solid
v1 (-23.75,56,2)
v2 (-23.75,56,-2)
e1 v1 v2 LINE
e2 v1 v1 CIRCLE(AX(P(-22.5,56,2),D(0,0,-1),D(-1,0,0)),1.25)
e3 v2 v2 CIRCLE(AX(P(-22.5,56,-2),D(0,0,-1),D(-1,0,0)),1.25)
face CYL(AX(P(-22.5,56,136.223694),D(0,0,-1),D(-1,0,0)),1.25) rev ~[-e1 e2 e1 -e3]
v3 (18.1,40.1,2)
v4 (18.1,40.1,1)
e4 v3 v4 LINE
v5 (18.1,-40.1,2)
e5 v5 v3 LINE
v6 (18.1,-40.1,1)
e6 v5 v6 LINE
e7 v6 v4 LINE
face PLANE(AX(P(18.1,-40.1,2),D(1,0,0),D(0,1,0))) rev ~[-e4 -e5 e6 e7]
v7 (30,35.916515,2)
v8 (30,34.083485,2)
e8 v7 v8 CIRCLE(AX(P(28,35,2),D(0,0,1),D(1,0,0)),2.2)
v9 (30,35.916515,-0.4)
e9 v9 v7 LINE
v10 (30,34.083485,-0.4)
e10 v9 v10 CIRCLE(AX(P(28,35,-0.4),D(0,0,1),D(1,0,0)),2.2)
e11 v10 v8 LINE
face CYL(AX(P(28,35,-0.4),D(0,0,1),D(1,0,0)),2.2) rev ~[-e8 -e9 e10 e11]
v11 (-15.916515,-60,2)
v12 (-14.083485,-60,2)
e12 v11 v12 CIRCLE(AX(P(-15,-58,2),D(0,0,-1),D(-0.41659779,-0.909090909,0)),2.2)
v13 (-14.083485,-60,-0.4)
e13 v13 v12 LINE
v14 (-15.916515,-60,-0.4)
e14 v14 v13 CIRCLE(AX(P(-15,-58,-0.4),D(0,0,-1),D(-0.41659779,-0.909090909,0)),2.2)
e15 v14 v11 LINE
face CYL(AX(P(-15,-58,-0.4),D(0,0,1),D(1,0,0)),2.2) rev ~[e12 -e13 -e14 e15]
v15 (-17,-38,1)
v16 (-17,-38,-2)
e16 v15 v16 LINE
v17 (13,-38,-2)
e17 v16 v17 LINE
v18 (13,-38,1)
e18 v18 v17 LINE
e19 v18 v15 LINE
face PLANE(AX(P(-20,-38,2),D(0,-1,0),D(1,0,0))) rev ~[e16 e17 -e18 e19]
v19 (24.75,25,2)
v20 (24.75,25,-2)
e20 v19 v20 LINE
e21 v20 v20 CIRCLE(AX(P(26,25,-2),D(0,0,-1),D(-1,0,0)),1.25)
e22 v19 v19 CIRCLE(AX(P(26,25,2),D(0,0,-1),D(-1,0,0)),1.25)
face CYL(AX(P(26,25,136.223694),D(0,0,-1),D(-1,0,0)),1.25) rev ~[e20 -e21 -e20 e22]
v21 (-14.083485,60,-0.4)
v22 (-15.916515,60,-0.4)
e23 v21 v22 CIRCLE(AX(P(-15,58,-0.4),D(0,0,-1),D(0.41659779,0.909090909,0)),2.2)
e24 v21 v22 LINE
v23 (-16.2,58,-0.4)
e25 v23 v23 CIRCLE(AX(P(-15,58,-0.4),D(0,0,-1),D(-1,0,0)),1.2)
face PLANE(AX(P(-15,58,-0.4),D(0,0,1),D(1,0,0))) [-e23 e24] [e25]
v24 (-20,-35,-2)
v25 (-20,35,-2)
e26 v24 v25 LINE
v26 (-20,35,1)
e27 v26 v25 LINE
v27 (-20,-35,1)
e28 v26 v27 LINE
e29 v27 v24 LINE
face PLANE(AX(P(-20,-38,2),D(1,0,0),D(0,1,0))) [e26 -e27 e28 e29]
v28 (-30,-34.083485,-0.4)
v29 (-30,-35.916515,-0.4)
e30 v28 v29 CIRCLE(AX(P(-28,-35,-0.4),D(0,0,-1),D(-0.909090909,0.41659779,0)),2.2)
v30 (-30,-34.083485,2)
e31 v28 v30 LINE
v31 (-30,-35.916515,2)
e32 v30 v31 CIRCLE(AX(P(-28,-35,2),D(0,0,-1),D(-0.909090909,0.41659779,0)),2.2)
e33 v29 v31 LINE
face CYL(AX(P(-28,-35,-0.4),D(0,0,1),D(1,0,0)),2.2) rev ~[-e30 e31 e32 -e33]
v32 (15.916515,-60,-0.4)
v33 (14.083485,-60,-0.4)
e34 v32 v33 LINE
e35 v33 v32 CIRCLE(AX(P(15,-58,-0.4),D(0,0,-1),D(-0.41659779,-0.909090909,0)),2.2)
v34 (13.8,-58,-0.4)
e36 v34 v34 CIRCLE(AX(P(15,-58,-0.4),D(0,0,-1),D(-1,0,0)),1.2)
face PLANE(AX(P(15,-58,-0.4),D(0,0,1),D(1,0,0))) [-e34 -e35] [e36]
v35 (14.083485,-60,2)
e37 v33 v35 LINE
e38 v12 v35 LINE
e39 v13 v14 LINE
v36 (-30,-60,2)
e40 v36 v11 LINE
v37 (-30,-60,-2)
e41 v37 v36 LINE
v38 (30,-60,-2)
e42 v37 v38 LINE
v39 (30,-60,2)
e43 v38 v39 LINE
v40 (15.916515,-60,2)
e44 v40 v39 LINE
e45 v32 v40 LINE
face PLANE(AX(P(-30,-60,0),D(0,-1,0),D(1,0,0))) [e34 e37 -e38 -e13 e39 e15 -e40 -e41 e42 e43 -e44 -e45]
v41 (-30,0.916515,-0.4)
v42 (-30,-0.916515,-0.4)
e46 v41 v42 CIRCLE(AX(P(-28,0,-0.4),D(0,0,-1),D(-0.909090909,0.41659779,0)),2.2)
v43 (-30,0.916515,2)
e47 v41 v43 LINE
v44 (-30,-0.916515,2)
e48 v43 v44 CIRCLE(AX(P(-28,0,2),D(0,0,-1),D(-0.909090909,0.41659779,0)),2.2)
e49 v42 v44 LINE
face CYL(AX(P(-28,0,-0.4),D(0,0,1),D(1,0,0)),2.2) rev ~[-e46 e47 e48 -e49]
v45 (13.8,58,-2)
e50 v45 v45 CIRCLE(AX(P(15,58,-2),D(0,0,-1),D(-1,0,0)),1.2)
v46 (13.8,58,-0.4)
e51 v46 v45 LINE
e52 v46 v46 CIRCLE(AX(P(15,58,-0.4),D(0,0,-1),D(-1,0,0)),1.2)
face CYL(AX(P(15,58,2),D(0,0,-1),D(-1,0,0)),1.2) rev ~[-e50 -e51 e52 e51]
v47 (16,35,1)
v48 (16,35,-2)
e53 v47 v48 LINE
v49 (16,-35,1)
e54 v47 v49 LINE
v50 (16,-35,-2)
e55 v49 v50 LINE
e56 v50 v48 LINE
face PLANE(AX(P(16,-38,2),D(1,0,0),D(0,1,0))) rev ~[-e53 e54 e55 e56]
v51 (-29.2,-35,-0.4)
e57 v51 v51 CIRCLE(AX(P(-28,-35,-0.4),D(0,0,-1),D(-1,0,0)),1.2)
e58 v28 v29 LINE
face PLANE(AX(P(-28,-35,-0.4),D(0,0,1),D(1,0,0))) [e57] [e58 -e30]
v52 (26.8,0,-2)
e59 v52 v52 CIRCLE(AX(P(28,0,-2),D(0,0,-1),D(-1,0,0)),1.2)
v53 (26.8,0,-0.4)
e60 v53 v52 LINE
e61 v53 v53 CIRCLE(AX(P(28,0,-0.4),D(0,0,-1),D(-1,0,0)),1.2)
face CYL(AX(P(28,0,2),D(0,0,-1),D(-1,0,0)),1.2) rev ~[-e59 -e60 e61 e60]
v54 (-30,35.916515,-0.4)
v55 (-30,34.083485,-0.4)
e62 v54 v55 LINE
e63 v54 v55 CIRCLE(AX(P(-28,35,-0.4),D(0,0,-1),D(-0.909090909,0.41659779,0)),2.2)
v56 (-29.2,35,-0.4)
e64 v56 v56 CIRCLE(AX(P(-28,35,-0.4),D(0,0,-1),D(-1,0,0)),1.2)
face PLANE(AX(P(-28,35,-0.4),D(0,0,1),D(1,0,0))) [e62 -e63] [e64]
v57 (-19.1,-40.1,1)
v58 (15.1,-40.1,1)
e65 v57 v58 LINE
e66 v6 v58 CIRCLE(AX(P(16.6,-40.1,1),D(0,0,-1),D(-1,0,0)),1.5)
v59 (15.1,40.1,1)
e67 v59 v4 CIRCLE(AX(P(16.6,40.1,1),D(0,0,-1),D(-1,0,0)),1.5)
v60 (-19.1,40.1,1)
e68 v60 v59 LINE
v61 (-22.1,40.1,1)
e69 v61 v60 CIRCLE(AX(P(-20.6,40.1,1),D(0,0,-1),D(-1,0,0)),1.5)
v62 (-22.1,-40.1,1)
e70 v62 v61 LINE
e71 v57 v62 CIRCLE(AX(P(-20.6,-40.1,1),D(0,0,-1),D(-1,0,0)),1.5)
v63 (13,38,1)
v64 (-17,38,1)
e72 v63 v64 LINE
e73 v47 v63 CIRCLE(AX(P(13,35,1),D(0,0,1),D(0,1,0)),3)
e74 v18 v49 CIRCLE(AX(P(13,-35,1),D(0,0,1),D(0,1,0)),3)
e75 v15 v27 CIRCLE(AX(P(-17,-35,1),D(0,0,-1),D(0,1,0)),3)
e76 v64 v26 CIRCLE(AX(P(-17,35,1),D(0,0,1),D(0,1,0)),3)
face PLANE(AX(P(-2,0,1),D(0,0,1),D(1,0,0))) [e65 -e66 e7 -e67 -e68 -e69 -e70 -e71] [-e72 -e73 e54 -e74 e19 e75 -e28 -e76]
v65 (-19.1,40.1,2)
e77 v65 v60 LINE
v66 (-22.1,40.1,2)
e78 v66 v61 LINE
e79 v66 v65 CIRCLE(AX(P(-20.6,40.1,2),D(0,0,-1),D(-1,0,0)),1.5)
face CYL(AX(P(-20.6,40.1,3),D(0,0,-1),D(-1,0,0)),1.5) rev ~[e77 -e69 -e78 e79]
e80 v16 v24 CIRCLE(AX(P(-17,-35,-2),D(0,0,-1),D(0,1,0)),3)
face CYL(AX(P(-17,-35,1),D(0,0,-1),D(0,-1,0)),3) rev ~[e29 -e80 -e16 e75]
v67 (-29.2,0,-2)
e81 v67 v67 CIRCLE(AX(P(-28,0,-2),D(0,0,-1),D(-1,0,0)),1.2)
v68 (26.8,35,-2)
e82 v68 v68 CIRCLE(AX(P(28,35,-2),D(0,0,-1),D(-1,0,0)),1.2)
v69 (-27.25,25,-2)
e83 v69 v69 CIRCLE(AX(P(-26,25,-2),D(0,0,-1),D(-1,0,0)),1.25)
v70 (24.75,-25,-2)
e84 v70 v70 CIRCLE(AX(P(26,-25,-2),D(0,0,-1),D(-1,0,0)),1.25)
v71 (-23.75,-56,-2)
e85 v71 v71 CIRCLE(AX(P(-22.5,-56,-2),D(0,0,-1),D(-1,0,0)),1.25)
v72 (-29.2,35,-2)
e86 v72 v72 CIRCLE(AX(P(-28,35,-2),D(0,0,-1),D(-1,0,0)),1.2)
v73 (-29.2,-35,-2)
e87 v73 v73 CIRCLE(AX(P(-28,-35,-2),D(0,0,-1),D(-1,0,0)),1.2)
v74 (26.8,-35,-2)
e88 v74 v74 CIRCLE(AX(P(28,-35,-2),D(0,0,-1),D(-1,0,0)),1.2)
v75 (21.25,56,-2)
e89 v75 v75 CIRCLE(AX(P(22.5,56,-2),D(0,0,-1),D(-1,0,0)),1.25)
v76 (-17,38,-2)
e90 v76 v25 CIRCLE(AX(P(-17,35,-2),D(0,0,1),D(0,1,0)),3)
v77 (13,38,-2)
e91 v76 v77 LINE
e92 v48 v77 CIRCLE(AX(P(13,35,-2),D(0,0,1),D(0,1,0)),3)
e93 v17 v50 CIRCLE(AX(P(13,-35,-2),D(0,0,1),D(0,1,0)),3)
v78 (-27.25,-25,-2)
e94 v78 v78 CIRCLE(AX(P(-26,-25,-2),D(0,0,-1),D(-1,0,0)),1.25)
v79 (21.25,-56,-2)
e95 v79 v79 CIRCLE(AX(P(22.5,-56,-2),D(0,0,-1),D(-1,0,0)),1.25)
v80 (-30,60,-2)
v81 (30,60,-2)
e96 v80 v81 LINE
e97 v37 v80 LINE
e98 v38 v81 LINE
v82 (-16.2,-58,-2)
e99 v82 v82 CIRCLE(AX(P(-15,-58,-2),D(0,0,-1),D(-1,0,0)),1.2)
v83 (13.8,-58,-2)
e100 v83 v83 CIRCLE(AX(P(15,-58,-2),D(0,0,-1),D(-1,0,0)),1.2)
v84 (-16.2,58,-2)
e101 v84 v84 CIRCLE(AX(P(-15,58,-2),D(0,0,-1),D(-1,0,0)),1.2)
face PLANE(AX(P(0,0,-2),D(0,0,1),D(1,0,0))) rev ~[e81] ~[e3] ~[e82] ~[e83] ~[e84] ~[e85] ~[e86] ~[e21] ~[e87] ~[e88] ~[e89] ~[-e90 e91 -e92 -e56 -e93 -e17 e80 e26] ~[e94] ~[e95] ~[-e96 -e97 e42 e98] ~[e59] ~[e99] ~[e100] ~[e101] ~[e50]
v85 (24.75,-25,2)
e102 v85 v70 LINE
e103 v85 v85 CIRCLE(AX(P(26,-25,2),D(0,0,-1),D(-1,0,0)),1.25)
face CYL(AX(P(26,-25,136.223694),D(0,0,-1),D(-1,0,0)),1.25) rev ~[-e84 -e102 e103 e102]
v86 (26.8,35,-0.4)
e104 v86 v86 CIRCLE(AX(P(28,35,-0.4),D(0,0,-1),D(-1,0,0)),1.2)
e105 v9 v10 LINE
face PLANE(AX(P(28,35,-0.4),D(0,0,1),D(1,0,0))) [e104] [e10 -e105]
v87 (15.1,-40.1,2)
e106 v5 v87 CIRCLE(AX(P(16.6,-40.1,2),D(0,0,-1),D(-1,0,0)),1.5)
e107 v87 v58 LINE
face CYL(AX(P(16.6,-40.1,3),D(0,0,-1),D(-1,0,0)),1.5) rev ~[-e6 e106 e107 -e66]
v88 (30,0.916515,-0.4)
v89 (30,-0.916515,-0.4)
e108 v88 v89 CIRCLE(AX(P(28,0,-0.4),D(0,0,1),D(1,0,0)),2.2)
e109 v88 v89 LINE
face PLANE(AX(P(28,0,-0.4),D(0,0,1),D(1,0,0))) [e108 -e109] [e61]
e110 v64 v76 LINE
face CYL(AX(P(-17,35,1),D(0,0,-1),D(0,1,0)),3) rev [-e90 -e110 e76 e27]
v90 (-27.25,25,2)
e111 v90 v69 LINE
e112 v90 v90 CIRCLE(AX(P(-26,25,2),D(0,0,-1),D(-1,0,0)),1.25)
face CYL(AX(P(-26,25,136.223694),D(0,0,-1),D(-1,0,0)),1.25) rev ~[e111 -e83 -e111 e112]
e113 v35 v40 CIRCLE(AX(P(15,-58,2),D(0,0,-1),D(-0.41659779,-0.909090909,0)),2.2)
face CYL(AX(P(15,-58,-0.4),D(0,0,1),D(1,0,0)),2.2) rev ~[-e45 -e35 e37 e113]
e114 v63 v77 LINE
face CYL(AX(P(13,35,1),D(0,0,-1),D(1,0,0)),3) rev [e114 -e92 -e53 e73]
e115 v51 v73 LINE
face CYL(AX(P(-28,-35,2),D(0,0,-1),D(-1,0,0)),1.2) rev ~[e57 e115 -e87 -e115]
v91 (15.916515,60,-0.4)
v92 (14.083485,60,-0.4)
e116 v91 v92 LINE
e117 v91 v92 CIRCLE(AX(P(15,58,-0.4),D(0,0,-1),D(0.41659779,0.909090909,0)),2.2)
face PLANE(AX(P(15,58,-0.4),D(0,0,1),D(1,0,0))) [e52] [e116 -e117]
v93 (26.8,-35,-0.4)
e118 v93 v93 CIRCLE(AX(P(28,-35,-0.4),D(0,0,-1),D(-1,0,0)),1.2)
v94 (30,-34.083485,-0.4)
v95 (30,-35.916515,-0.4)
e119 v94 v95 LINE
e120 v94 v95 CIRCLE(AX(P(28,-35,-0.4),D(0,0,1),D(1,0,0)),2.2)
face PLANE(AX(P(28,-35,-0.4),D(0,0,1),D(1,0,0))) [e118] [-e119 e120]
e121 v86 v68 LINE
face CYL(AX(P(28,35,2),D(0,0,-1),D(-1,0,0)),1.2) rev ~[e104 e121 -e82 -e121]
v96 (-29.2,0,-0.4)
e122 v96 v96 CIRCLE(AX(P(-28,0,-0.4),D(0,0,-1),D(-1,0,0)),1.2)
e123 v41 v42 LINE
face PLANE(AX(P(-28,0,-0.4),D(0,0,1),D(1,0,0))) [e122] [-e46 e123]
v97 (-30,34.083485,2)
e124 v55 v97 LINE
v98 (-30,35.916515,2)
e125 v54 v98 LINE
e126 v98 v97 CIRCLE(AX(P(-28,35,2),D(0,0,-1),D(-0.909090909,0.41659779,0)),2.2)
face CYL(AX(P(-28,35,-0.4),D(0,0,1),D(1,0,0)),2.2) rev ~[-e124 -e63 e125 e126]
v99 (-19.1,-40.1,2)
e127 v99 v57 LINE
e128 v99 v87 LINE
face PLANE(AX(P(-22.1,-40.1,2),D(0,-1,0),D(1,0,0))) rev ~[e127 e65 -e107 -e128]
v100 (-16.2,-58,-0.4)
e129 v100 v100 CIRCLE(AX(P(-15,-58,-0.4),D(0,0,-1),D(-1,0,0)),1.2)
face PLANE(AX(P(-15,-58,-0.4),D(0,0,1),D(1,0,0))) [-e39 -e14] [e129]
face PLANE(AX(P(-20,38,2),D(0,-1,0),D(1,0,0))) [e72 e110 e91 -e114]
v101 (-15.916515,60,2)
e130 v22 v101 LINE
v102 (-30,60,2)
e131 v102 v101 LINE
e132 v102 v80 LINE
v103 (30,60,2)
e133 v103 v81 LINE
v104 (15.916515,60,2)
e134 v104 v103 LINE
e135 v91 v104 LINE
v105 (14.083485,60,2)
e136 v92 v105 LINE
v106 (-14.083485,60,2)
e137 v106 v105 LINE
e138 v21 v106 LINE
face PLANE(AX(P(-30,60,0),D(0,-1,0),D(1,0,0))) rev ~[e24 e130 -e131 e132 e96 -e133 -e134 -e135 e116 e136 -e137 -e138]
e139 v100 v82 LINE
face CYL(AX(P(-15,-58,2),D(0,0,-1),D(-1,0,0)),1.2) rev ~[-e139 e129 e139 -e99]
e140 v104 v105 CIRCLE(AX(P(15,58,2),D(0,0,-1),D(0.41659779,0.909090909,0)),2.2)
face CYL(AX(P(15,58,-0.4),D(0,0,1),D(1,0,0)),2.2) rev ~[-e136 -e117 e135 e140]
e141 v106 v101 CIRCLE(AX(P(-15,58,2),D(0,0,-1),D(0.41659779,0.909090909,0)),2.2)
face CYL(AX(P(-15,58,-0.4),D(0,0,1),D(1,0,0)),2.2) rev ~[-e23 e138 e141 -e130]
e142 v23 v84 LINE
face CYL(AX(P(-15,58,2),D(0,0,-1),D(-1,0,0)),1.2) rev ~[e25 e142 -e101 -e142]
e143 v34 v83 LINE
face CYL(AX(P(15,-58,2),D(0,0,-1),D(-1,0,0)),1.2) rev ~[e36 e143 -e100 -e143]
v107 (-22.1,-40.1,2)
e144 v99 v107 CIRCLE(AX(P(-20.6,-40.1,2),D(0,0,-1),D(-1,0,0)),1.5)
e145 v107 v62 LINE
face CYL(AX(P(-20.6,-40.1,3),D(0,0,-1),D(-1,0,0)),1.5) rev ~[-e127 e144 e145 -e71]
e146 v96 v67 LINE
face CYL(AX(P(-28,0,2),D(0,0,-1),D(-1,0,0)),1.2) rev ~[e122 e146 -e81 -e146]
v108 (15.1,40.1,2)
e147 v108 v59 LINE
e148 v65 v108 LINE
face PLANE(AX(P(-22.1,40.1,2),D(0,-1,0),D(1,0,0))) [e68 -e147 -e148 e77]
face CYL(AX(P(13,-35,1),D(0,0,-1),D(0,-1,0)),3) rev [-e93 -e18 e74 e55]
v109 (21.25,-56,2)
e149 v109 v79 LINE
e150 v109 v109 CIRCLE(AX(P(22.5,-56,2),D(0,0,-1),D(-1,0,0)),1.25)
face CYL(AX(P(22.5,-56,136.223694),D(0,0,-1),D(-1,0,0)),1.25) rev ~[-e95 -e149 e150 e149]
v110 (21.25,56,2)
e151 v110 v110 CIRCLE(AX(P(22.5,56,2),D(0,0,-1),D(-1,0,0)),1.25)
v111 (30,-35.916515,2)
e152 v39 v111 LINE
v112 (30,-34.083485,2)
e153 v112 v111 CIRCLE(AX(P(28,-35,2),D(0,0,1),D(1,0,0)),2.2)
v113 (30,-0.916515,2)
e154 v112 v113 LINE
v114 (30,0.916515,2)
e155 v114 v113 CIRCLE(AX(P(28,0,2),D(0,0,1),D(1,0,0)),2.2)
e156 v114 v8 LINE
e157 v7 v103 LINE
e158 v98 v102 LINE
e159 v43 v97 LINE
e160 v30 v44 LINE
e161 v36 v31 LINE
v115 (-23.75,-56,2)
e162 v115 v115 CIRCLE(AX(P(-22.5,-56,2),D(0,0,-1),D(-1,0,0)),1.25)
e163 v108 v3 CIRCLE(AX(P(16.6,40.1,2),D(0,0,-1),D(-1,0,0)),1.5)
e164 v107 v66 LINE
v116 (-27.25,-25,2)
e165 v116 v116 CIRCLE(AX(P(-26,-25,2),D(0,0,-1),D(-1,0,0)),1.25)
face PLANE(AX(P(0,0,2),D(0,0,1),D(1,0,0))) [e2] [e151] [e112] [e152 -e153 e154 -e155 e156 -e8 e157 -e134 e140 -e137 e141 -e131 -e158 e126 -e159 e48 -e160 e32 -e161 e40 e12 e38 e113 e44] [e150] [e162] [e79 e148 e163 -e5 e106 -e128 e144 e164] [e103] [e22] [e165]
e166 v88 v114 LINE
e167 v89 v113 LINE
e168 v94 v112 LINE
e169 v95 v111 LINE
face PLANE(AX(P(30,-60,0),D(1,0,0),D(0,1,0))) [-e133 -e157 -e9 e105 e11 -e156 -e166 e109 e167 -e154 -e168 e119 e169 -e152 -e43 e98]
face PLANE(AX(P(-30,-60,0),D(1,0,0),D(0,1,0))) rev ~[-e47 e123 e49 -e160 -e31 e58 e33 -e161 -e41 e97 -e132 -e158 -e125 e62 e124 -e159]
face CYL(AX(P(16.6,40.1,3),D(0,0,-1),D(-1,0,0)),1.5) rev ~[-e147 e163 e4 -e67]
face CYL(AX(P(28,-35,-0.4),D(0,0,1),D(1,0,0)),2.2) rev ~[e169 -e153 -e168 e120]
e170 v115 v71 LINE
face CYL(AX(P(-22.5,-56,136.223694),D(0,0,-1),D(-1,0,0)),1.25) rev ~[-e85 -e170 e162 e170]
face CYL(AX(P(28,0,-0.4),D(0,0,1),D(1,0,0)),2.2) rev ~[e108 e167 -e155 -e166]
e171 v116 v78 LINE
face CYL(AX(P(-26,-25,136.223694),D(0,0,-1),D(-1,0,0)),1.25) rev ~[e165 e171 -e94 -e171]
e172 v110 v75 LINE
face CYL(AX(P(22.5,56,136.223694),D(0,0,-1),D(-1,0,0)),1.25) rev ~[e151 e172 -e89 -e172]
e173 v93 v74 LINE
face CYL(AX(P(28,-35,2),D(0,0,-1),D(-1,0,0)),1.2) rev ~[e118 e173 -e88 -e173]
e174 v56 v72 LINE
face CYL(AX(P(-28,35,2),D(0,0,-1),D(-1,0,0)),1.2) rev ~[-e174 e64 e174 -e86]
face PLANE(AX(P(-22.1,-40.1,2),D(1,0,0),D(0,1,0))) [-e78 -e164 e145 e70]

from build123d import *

# Parameters (mm, degrees)
SKETCH_1_W                   = 60
SKETCH_1_H                   = 120
EXTRUDE_1_DEPTH              = 2
SKETCH_2_W                   = 36
SKETCH_2_H                   = 76
CUT_EXTRUDE_1_DEPTH          = 68.201190466
SKETCH_3_W                   = 40.2
SKETCH_3_H                   = 80.2
CUT_EXTRUDE_2_DEPTH          = 1
HOLE_WIZARD_3_0_3_1_D        = 3
HOLE_WIZARD_3_0_3_1_DEPTH    = 1
FILLET_1_R                   = 3
HOLE_WIZARD_M2_1_D           = 2.4
HOLE_WIZARD_M2_1_CBORE_D     = 4.4
HOLE_WIZARD_M2_1_CBORE_DEPTH = 2.4
HOLE_WIZARD_M3_1_D           = 2.5


with BuildPart() as part:
    # 草图1 → 凸台-拉伸1 (new, symmetric)
    with BuildSketch(Plane.XY):
        Rectangle(SKETCH_1_W, SKETCH_1_H)
    extrude(amount=EXTRUDE_1_DEPTH, both=True)

    # 草图2 → 切除-拉伸1 (cut, through all)
    with BuildSketch(Plane.XY.offset(2)):
        with Locations((-2, 0)):
            Rectangle(SKETCH_2_W, SKETCH_2_H)
    extrude(amount=-CUT_EXTRUDE_1_DEPTH, mode=Mode.SUBTRACT)

    # 草图3 → 切除-拉伸2 (cut)
    with BuildSketch(Plane.XY.offset(2)):
        with Locations((-2, 0)):
            Rectangle(SKETCH_3_W, SKETCH_3_H)
    extrude(amount=-CUT_EXTRUDE_2_DEPTH, mode=Mode.SUBTRACT)

    # Ø3.0 (3) 直径孔1
    with Locations(Plane.XY.offset(2)):
        with Locations((-20.6, 40.1), (16.6, 40.1), (16.6, -40.1), (-20.6, -40.1)):
            Hole(HOLE_WIZARD_3_0_3_1_D / 2, depth=HOLE_WIZARD_3_0_3_1_DEPTH)

    # 圆角1
    fillet_1_edges = [part.edges().sort_by_distance(p)[0] for p in [
        (-20, -38, -0.5),
        (-20, 38, -0.5),
        (16, 38, -0.5),
        (16, -38, -0.5),
    ]]
    fillet(fillet_1_edges, radius=FILLET_1_R)

    # M2 六角凹头螺钉的柱形沉头孔1 (through all)
    with Locations(Plane.XY.offset(2)):
        with Locations((-28, 0), (28, 0), (-15, 58), (15, 58), (-28, 35), (28, 35), (-28, -35), (28, -35), (-15, -58), (15, -58)):
            CounterBoreHole(HOLE_WIZARD_M2_1_D / 2, HOLE_WIZARD_M2_1_CBORE_D / 2, HOLE_WIZARD_M2_1_CBORE_DEPTH)

    # M3 螺纹孔1 (through all)
    with Locations(Plane.XY.offset(2)):
        with Locations((-22.5, 56), (22.5, 56), (-26, 25), (26, 25), (26, -25), (-26, -25), (22.5, -56), (-22.5, -56)):
            Hole(HOLE_WIZARD_M3_1_D / 2)


solid = part.part
